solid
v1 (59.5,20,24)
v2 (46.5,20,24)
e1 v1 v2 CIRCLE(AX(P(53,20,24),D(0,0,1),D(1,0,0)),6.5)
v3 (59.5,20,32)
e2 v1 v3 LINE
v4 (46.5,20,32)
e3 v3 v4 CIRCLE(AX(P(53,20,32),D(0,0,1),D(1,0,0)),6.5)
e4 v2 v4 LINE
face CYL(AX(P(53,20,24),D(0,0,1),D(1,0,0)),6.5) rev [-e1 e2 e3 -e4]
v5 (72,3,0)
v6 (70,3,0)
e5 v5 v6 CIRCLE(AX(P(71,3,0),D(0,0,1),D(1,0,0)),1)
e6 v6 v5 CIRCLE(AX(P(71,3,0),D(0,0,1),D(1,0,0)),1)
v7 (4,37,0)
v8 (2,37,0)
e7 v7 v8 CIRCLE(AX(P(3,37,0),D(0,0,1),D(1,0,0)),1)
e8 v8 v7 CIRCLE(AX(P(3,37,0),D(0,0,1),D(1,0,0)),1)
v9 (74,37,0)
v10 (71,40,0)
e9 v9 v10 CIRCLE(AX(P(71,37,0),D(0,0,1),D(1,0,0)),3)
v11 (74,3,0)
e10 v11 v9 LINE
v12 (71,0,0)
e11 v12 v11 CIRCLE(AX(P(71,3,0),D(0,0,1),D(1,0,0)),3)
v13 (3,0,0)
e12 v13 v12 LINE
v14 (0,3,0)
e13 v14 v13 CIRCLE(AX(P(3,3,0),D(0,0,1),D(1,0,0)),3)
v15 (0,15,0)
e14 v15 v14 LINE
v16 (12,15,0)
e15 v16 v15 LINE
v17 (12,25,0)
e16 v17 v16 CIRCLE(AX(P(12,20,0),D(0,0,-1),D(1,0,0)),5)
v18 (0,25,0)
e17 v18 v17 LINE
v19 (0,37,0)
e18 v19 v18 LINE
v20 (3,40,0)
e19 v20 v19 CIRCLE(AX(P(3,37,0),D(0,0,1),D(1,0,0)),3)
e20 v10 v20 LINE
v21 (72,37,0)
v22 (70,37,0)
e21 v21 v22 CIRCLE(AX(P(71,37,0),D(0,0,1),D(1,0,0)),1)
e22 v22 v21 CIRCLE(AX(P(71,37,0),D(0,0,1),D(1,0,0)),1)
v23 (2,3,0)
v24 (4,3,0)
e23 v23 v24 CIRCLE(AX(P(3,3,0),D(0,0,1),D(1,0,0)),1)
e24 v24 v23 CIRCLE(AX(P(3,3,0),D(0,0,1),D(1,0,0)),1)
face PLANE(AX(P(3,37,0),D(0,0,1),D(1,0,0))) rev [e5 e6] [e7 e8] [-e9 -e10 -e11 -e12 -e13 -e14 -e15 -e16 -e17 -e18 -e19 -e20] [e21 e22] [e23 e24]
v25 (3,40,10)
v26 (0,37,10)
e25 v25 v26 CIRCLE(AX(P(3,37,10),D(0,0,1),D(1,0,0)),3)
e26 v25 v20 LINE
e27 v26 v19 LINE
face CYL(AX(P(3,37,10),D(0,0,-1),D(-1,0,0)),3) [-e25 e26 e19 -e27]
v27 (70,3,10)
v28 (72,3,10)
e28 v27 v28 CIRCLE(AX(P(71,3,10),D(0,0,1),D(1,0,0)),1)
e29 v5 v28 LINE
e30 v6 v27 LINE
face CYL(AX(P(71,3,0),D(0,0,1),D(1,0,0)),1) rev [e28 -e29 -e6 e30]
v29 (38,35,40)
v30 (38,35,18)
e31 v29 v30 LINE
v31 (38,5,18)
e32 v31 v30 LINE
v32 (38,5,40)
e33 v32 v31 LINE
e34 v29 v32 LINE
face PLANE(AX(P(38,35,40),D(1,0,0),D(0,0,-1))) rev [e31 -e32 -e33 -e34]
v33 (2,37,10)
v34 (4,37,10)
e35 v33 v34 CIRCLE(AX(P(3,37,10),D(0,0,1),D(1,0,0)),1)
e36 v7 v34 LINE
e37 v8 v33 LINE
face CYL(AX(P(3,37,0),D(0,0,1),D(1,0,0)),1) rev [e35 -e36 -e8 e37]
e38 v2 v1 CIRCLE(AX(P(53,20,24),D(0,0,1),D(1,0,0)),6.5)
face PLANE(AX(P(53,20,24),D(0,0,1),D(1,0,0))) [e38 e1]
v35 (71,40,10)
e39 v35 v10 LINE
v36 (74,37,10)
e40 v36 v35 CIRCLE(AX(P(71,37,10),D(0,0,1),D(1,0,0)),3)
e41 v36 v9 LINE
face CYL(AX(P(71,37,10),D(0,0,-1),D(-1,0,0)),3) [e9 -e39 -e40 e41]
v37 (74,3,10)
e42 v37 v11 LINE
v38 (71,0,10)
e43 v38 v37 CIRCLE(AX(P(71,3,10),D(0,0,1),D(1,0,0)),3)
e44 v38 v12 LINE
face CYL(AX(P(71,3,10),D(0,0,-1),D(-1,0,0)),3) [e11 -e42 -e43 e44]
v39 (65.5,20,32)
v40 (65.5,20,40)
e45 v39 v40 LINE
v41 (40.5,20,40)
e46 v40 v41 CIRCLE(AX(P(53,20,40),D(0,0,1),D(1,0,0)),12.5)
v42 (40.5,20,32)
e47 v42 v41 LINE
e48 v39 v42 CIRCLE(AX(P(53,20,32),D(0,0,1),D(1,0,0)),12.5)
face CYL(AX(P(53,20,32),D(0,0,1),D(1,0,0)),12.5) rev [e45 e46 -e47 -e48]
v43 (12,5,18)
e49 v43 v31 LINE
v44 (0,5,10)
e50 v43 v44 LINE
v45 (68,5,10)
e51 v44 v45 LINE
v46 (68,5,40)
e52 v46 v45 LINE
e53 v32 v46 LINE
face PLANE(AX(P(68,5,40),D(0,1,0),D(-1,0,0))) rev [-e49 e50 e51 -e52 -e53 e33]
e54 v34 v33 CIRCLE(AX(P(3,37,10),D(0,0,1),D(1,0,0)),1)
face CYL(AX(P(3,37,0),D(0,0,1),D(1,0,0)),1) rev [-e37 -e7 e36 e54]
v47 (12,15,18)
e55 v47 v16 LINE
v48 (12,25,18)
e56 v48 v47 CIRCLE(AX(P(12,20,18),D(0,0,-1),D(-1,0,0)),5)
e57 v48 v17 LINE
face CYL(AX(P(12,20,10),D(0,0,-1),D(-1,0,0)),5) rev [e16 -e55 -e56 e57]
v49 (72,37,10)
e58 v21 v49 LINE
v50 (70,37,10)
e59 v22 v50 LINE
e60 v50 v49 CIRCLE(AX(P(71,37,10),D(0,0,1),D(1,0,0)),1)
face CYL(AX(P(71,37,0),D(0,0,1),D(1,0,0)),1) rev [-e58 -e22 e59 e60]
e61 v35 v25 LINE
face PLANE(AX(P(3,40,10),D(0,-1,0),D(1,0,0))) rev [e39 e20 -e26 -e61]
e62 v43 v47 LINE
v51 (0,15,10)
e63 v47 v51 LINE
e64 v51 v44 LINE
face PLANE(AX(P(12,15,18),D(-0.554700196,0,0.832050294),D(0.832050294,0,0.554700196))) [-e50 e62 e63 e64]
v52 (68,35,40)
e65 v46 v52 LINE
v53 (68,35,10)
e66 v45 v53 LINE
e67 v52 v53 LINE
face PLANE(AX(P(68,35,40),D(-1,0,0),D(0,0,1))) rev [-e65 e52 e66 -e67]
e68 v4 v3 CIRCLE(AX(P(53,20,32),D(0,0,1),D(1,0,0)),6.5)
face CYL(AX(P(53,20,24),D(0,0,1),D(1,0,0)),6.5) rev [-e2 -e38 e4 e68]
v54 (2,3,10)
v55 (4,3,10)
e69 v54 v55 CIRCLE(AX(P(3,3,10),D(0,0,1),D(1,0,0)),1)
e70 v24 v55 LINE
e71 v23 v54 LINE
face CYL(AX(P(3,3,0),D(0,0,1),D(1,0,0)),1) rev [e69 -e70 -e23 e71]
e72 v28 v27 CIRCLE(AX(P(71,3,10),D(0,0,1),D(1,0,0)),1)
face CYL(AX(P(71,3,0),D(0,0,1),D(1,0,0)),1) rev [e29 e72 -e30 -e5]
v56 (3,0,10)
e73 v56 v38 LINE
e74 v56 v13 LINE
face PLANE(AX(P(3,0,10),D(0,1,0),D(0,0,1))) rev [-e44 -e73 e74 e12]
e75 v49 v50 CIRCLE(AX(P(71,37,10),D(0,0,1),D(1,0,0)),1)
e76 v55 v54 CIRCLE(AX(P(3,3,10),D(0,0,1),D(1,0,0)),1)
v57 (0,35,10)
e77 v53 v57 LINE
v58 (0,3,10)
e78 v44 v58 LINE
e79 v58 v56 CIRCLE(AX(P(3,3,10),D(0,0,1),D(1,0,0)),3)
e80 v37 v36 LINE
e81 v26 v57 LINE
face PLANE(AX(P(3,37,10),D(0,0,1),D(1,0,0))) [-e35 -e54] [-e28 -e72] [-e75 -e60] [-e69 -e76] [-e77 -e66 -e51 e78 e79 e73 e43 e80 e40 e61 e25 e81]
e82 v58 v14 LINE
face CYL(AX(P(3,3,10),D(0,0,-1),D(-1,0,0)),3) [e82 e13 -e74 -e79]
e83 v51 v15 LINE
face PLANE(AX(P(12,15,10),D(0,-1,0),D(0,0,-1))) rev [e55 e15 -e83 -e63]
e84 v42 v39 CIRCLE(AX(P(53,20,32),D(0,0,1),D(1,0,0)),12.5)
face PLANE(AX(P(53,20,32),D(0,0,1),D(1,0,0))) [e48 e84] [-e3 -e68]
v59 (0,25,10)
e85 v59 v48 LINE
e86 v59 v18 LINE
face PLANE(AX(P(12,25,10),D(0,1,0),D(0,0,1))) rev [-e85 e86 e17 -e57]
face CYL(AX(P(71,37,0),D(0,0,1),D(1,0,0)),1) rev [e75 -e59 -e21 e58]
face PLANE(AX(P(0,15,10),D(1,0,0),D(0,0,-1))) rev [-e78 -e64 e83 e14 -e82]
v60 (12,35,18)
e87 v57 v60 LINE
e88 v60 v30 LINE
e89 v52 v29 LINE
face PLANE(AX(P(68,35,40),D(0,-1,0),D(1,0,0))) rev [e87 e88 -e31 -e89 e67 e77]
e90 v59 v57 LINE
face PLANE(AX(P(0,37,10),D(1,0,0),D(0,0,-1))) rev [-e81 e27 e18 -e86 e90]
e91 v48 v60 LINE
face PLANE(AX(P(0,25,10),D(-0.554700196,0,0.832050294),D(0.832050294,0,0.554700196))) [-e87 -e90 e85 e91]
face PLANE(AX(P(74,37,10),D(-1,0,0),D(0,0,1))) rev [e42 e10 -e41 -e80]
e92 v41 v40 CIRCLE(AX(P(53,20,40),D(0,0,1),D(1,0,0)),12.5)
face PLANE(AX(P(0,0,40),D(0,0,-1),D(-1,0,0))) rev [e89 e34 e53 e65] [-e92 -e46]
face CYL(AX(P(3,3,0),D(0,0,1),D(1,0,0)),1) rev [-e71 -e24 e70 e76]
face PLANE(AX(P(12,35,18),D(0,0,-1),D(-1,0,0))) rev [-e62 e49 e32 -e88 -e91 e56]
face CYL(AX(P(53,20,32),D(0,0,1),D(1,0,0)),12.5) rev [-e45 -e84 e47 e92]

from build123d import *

# Parameters (mm, degrees)
MOUNTING_FLANGE_DEPTH    = 10
HOUSING_BLOCK_PROFILE_W  = 30
HOUSING_BLOCK_PROFILE_H  = 30
HOUSING_BLOCK_DEPTH      = 30
UPPER_BLOCK_PROFILE_W    = 8
UPPER_BLOCK_PROFILE_H    = 30
UPPER_BLOCK_DEPTH        = 26
SIDE_RELIEF_CUT_DEPTH    = 8
GUSSET_A_DEPTH           = 10
GUSSET_B_DEPTH           = 10
MOUNTING_HOLES_PROFILE_R = 1
MOUNTING_HOLES_4X_DEPTH  = 10
COUNTERBORE_25_PROFILE_R = 12.5
COUNTERBORE_25_DEPTH     = 8
BORE_13_PROFILE_R        = 6.5
BORE_13_DEPTH            = 8


with BuildPart() as part:
    # Flange Profile → Mounting Flange (new body)
    with BuildSketch(Plane.XY):
        with BuildLine():
            Line((3, 0), (71, 0))
            ThreePointArc((71, 0), (73.121320344, 0.878679656), (74, 3))
            Line((74, 3), (74, 37))
            ThreePointArc((74, 37), (73.121320344, 39.121320344), (71, 40))
            Line((71, 40), (3, 40))
            ThreePointArc((3, 40), (0.878679656, 39.121320344), (0, 37))
            Line((0, 37), (0, 25))
            Line((0, 25), (12, 25))
            ThreePointArc((12, 25), (17, 20), (12, 15))
            Line((12, 15), (0, 15))
            Line((0, 15), (0, 3))
            ThreePointArc((0, 3), (0.878679656, 0.878679656), (3, 0))
        make_face()
    extrude(amount=MOUNTING_FLANGE_DEPTH)

    # Housing Block Profile → Housing Block (add)
    with BuildSketch(Plane.XY.offset(10)):
        with Locations((53, 20)):
            Rectangle(HOUSING_BLOCK_PROFILE_W, HOUSING_BLOCK_PROFILE_H)
    extrude(amount=HOUSING_BLOCK_DEPTH)

    # Upper Block Profile → Upper Block (add)
    with BuildSketch(Plane.ZY.offset(-38)):
        with Locations((14, 20)):
            Rectangle(UPPER_BLOCK_PROFILE_W, UPPER_BLOCK_PROFILE_H)
    extrude(amount=UPPER_BLOCK_DEPTH)

    # Side Relief Profile → Side Relief Cut (cut)
    with BuildSketch(Plane(origin=(0, 0, 10), x_dir=(-1, 0, 0), z_dir=(0, 0, -1))):
        with BuildLine():
            Line((-12, 25), (-12, 15))
            ThreePointArc((-12, 15), (-17, 20), (-12, 25))
        make_face()
    extrude(amount=-SIDE_RELIEF_CUT_DEPTH, mode=Mode.SUBTRACT)

    # Gusset A Profile → Gusset A (add)
    with BuildSketch(Plane.XZ.offset(-5)):
        Polygon((12, 10), (12, 18), (0, 10), align=None)
    extrude(amount=-GUSSET_A_DEPTH)

    # Gusset B Profile → Gusset B (add)
    with BuildSketch(Plane(origin=(0, 35, 0), x_dir=(1, 0, 0), z_dir=(0, 1, 0))):
        Polygon((12, -18), (12, -10), (0, -10), align=None)
    extrude(amount=-GUSSET_B_DEPTH)

    # Mounting Holes Profile → Mounting Holes 4x (cut)
    with BuildSketch(Plane.XY.offset(10)):
        with Locations((3, 37)):
            Circle(MOUNTING_HOLES_PROFILE_R)
        with Locations((71, 37)):
            Circle(MOUNTING_HOLES_PROFILE_R)
        with Locations((71, 3)):
            Circle(MOUNTING_HOLES_PROFILE_R)
        with Locations((3, 3)):
            Circle(MOUNTING_HOLES_PROFILE_R)
    extrude(amount=-MOUNTING_HOLES_4X_DEPTH, mode=Mode.SUBTRACT)

    # Counterbore Ø25 Profile → Counterbore Ø25 (cut)
    with BuildSketch(Plane.XY.offset(40)):
        with Locations((53, 20)):
            Circle(COUNTERBORE_25_PROFILE_R)
    extrude(amount=-COUNTERBORE_25_DEPTH, mode=Mode.SUBTRACT)

    # Bore Ø13 Profile → Bore Ø13 (cut)
    with BuildSketch(Plane.XY.offset(32)):
        with Locations((53, 20)):
            Circle(BORE_13_PROFILE_R)
    extrude(amount=-BORE_13_DEPTH, mode=Mode.SUBTRACT)


solid = part.part
